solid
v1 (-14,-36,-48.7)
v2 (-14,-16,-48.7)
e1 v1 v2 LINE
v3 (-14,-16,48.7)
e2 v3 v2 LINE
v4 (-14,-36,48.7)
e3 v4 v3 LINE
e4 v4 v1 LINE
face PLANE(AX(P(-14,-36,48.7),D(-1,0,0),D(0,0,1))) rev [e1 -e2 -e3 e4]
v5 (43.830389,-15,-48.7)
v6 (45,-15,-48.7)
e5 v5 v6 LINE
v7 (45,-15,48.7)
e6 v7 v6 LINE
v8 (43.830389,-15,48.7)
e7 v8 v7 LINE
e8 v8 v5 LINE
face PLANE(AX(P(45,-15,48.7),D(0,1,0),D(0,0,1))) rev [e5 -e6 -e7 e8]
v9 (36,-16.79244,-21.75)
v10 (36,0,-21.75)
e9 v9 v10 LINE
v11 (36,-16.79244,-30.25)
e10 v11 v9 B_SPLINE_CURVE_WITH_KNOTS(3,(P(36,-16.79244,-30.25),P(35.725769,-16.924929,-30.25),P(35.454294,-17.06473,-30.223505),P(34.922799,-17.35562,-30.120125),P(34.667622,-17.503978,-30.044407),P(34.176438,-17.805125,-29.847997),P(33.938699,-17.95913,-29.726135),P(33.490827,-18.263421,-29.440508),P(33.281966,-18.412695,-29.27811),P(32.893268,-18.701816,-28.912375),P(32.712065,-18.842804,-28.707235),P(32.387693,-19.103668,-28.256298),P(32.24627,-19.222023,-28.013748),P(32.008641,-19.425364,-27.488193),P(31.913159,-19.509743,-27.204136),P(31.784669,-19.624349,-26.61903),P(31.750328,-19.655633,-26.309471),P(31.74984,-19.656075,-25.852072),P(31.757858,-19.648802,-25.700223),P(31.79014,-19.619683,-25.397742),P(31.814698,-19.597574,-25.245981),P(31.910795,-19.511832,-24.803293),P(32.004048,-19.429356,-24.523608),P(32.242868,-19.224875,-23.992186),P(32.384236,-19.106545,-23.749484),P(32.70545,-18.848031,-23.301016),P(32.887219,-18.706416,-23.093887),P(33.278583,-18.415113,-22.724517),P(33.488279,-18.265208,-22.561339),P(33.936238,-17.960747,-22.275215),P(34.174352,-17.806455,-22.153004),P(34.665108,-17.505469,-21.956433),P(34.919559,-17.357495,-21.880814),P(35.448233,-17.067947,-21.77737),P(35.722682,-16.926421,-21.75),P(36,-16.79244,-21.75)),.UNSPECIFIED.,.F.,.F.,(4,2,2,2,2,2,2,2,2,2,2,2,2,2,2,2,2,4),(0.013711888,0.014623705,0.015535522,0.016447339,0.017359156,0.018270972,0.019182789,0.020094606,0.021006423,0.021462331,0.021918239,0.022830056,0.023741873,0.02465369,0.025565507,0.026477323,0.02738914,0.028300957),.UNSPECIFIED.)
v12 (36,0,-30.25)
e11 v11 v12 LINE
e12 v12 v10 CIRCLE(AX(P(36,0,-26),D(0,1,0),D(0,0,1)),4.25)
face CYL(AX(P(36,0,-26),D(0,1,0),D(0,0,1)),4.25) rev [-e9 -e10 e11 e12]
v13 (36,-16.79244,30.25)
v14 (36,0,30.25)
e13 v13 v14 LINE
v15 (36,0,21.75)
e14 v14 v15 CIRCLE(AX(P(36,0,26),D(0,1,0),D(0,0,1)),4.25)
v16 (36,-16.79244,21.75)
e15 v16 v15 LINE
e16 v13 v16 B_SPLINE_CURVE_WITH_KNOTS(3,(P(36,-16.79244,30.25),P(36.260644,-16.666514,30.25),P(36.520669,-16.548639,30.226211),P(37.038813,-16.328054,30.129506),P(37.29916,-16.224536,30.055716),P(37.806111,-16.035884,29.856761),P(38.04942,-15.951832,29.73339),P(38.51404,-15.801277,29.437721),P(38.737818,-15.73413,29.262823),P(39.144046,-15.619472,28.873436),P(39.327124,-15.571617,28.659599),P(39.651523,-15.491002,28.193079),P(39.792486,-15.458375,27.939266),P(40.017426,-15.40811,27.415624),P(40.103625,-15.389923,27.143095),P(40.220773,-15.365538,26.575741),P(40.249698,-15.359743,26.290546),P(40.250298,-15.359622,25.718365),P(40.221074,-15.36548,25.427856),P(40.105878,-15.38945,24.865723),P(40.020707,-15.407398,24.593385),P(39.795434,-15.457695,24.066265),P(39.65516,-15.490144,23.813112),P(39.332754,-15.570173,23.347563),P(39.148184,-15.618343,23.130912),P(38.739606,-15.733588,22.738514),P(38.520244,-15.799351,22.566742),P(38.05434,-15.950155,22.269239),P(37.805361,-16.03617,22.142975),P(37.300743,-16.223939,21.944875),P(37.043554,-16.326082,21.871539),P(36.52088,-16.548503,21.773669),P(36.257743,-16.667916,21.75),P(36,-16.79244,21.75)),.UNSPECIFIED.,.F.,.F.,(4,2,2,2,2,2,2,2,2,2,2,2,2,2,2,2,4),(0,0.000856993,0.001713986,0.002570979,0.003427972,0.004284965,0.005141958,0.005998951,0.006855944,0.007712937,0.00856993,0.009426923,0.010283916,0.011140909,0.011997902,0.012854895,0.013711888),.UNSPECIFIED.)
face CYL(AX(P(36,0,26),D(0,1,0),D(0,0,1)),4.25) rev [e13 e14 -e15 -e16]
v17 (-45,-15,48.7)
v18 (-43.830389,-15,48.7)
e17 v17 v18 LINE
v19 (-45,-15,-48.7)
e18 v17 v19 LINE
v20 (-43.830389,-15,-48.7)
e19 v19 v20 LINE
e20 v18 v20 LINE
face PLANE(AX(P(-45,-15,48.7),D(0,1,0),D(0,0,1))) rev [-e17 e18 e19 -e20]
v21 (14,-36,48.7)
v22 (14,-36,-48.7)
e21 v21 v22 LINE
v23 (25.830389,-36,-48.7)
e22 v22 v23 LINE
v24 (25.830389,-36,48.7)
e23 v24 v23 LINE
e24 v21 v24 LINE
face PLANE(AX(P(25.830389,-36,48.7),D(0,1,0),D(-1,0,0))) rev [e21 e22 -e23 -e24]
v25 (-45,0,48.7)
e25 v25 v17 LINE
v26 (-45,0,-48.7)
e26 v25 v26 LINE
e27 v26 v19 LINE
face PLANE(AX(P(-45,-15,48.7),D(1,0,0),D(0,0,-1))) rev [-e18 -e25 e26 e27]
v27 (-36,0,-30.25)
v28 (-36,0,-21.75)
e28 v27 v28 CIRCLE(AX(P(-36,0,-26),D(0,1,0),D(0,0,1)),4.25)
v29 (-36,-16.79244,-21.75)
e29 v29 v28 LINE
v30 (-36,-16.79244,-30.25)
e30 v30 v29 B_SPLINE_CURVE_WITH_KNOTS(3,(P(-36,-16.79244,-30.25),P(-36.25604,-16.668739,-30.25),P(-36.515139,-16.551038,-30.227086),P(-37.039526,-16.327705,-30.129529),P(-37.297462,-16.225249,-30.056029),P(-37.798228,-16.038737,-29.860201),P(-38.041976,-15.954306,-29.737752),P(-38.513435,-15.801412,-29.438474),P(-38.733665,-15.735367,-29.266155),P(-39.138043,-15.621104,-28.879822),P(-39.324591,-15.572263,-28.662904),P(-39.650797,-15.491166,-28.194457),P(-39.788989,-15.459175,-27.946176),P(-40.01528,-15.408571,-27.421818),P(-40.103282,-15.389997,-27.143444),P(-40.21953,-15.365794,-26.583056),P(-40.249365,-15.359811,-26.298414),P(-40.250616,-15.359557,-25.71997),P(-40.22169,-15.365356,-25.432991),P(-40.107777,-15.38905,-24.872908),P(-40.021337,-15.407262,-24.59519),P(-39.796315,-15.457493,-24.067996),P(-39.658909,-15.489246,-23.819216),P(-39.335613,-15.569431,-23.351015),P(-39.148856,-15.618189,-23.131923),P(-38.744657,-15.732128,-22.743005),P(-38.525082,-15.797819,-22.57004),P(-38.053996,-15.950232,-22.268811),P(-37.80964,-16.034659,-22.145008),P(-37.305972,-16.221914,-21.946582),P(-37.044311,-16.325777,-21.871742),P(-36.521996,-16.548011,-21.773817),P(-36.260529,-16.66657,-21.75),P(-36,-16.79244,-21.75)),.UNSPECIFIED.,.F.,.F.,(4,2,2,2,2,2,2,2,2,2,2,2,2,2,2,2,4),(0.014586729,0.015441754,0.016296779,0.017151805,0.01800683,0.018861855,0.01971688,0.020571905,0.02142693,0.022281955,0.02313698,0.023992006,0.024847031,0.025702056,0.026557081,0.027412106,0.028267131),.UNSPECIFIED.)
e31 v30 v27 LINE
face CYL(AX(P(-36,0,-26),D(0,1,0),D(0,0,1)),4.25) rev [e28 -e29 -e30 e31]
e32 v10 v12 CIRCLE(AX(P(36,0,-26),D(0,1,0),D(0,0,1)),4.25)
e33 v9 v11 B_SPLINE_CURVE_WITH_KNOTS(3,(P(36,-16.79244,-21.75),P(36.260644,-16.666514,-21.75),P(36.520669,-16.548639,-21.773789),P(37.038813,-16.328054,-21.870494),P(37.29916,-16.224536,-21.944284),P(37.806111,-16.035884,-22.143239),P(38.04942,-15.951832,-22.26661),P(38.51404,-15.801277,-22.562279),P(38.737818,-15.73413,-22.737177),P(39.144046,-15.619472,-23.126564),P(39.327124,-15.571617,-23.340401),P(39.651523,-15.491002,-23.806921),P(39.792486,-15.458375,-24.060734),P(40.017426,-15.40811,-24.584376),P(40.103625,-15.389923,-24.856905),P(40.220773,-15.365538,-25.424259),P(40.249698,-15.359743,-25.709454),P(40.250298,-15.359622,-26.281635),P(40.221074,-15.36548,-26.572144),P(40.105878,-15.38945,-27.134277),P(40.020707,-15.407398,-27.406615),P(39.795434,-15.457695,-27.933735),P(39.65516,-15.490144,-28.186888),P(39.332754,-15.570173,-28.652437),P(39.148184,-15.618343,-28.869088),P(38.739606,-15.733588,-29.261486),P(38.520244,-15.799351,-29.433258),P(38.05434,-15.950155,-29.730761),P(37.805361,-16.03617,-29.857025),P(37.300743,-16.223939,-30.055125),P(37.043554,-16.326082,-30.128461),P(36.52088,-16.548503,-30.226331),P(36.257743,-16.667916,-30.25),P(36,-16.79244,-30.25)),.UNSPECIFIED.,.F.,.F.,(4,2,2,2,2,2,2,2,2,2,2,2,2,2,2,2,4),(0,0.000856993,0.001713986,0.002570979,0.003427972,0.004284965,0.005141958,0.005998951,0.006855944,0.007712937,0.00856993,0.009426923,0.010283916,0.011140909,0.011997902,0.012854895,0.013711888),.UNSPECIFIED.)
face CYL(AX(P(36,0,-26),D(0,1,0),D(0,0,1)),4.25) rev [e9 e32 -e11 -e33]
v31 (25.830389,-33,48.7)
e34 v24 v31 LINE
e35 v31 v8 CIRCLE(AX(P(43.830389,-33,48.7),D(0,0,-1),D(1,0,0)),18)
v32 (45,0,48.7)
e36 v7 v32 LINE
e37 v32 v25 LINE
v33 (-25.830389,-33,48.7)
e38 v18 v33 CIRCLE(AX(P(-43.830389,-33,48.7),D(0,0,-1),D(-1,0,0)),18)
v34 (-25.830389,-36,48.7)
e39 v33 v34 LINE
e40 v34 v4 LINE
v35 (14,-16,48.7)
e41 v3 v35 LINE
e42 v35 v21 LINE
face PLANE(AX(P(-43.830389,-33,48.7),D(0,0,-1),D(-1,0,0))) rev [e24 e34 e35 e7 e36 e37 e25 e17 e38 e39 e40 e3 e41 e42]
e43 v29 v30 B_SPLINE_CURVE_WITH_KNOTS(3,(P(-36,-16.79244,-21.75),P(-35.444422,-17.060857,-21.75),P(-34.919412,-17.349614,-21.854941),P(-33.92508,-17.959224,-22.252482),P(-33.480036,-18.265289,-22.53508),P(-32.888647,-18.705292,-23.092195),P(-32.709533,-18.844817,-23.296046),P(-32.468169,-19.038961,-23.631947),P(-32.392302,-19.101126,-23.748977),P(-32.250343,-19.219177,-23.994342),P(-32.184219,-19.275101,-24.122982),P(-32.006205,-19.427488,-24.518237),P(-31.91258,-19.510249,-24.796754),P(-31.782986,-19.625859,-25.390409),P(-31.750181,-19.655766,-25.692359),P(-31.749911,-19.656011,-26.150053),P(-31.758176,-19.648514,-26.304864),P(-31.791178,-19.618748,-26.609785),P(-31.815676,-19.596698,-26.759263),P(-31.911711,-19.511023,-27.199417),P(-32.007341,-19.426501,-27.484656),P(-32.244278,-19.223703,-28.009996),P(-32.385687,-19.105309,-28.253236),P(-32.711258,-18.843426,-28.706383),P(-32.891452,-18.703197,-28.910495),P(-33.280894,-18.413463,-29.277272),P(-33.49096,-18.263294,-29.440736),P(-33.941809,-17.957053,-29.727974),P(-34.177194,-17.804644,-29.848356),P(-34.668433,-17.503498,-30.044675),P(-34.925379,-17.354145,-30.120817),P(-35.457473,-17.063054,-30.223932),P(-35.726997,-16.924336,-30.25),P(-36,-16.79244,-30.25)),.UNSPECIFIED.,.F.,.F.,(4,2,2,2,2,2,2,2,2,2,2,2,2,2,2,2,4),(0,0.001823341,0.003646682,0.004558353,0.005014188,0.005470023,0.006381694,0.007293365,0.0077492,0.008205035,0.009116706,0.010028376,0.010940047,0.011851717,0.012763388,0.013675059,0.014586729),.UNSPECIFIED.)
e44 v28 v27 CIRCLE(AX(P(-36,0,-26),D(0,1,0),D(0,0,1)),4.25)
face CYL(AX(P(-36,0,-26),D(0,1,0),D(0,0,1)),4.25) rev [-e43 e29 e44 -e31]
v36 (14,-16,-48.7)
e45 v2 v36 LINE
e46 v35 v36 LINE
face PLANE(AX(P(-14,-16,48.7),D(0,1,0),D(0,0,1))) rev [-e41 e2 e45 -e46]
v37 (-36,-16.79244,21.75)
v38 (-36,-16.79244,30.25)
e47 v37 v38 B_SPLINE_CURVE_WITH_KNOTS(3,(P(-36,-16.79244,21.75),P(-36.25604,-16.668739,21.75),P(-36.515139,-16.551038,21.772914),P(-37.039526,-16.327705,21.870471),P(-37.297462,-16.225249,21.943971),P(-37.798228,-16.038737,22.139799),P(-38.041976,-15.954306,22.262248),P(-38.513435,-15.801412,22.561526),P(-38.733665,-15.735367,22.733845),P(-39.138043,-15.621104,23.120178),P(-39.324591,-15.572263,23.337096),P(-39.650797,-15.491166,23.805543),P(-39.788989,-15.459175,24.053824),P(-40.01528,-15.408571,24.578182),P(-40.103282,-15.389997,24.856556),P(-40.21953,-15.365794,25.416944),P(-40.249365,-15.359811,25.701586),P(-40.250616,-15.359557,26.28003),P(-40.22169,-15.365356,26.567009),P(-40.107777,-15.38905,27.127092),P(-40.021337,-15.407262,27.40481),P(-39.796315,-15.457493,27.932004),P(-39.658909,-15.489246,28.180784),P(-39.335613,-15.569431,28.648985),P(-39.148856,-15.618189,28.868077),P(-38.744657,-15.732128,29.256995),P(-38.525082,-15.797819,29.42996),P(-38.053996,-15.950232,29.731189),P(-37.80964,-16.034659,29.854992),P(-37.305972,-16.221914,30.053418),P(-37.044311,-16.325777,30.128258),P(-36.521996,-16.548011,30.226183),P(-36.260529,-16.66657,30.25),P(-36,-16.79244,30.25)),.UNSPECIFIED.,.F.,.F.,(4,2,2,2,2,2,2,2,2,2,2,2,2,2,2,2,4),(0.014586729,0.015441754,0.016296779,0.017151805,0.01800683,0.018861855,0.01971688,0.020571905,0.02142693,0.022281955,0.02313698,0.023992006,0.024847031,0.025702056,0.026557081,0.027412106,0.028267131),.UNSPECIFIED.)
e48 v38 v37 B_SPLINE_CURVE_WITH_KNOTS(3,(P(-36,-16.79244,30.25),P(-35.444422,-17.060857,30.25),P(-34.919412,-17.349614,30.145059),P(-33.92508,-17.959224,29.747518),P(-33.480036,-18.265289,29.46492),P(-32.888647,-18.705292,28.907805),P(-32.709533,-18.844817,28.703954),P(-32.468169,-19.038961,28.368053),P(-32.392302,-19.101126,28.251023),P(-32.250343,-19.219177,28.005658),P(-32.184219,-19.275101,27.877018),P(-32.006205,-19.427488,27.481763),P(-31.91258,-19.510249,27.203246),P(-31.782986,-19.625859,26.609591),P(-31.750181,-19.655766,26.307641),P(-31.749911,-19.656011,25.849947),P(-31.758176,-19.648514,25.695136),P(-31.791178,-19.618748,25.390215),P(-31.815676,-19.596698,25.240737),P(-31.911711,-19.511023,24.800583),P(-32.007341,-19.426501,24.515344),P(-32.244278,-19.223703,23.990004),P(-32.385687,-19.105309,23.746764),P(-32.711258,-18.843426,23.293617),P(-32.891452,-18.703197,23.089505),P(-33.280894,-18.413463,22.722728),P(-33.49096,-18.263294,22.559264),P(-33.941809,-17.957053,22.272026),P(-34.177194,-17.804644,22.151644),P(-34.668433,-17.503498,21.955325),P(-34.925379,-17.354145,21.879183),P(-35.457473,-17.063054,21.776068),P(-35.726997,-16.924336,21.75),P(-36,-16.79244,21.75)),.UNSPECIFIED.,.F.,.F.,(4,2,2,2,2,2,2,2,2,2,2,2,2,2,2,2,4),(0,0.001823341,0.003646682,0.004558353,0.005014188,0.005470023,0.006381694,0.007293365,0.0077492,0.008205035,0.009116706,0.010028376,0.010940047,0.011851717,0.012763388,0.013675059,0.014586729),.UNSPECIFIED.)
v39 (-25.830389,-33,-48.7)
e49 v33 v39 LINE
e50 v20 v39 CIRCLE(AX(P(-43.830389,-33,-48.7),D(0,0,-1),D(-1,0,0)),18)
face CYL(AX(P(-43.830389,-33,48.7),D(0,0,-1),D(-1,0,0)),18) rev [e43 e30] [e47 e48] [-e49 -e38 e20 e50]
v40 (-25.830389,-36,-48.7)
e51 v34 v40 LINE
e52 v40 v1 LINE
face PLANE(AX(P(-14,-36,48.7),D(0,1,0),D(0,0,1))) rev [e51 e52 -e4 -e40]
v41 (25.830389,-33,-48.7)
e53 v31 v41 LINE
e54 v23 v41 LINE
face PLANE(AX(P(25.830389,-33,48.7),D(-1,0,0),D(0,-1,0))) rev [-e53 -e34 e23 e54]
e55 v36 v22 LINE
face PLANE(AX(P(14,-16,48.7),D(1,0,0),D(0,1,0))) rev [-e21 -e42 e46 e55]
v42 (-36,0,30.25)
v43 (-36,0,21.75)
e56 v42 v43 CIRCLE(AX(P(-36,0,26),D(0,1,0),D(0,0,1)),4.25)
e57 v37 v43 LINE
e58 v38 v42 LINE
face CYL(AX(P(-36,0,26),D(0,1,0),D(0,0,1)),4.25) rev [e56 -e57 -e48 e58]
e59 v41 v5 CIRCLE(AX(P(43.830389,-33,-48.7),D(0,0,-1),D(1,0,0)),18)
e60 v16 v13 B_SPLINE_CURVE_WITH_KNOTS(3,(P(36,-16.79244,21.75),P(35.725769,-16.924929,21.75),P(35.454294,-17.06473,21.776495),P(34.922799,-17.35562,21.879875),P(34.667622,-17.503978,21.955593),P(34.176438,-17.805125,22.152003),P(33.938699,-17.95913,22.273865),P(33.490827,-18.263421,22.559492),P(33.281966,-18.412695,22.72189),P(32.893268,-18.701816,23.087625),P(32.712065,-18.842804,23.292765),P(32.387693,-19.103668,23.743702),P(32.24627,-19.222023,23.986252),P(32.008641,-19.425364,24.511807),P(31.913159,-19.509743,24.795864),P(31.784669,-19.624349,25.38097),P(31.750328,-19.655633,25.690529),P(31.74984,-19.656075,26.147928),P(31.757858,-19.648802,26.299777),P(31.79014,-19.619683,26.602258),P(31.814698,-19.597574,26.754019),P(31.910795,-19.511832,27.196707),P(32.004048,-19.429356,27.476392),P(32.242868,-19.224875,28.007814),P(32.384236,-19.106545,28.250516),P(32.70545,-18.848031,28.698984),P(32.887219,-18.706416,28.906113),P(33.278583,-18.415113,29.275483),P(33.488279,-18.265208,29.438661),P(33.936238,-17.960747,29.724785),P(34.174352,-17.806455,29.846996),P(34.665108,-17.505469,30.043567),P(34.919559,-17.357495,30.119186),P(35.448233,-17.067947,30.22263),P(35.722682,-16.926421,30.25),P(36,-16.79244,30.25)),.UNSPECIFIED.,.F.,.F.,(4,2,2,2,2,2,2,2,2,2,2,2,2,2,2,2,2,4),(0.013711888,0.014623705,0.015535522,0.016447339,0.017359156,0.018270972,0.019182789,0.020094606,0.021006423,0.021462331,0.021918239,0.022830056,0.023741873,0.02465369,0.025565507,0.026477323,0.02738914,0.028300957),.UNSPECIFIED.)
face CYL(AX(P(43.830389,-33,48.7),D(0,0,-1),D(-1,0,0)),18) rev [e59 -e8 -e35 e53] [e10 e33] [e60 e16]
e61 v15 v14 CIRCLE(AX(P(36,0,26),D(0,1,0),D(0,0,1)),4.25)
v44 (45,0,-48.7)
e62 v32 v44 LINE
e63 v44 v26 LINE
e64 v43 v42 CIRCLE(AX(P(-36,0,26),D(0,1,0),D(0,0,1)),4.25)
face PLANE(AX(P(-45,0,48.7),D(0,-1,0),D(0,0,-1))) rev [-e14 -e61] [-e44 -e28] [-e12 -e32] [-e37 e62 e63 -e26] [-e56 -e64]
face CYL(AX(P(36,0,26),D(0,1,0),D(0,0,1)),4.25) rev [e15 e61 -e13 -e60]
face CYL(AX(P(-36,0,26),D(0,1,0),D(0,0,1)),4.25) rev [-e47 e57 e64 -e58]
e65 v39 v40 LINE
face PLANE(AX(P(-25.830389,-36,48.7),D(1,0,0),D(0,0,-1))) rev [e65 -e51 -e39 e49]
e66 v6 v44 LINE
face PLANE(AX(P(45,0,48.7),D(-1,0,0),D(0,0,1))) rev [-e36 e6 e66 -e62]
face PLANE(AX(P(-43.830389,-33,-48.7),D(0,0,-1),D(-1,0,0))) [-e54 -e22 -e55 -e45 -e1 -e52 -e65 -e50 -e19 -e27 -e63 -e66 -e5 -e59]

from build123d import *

# Parameters (mm, degrees)
BOSS_EXTRUDE1_DEPTH    = 48.7
M10_TAPPED_HOLE1_D     = 8.5
M10_TAPPED_HOLE1_DEPTH = 24.5
M10_TAPPED_HOLE1_TIP   = 2.553657631


with BuildPart() as part:
    # Sketch1 → Boss-Extrude1 (new, symmetric)
    with BuildSketch(Plane.XY):
        with BuildLine():
            Line((-25.830388506, -36), (-25.830388506, -33))
            ThreePointArc((-25.830388506, -33), (-31.102466444, -20.272077939), (-43.830388506, -15))
            Line((-43.830388506, -15), (-45, -15))
            Line((-45, -15), (-45, 0))
            Line((-45, 0), (45, 0))
            Line((45, 0), (45, -15))
            Line((45, -15), (43.830388506, -15))
            ThreePointArc((43.830388506, -15), (31.102466444, -20.272077939), (25.830388506, -33))
            Line((25.830388506, -33), (25.830388506, -36))
            Line((25.830388506, -36), (14, -36))
            Line((14, -36), (14, -16))
            Line((14, -16), (-14, -16))
            Line((-14, -16), (-14, -36))
            Line((-14, -36), (-25.830388506, -36))
        make_face()
    extrude(amount=BOSS_EXTRUDE1_DEPTH, both=True)

    # M10 Tapped Hole1
    with Locations(Plane(origin=(0, 0, 0), x_dir=(-1, 0, 0), z_dir=(0, 1, 0))):
        with Locations((-36, 26), (36, 26), (-36, -26), (36, -26)):
            Hole(M10_TAPPED_HOLE1_D / 2, depth=M10_TAPPED_HOLE1_DEPTH)
            with Locations((0, 0, -(M10_TAPPED_HOLE1_DEPTH + M10_TAPPED_HOLE1_TIP / 2))):  # 118° drill point
                Cone(0, M10_TAPPED_HOLE1_D / 2, M10_TAPPED_HOLE1_TIP, mode=Mode.SUBTRACT)


solid = part.part
